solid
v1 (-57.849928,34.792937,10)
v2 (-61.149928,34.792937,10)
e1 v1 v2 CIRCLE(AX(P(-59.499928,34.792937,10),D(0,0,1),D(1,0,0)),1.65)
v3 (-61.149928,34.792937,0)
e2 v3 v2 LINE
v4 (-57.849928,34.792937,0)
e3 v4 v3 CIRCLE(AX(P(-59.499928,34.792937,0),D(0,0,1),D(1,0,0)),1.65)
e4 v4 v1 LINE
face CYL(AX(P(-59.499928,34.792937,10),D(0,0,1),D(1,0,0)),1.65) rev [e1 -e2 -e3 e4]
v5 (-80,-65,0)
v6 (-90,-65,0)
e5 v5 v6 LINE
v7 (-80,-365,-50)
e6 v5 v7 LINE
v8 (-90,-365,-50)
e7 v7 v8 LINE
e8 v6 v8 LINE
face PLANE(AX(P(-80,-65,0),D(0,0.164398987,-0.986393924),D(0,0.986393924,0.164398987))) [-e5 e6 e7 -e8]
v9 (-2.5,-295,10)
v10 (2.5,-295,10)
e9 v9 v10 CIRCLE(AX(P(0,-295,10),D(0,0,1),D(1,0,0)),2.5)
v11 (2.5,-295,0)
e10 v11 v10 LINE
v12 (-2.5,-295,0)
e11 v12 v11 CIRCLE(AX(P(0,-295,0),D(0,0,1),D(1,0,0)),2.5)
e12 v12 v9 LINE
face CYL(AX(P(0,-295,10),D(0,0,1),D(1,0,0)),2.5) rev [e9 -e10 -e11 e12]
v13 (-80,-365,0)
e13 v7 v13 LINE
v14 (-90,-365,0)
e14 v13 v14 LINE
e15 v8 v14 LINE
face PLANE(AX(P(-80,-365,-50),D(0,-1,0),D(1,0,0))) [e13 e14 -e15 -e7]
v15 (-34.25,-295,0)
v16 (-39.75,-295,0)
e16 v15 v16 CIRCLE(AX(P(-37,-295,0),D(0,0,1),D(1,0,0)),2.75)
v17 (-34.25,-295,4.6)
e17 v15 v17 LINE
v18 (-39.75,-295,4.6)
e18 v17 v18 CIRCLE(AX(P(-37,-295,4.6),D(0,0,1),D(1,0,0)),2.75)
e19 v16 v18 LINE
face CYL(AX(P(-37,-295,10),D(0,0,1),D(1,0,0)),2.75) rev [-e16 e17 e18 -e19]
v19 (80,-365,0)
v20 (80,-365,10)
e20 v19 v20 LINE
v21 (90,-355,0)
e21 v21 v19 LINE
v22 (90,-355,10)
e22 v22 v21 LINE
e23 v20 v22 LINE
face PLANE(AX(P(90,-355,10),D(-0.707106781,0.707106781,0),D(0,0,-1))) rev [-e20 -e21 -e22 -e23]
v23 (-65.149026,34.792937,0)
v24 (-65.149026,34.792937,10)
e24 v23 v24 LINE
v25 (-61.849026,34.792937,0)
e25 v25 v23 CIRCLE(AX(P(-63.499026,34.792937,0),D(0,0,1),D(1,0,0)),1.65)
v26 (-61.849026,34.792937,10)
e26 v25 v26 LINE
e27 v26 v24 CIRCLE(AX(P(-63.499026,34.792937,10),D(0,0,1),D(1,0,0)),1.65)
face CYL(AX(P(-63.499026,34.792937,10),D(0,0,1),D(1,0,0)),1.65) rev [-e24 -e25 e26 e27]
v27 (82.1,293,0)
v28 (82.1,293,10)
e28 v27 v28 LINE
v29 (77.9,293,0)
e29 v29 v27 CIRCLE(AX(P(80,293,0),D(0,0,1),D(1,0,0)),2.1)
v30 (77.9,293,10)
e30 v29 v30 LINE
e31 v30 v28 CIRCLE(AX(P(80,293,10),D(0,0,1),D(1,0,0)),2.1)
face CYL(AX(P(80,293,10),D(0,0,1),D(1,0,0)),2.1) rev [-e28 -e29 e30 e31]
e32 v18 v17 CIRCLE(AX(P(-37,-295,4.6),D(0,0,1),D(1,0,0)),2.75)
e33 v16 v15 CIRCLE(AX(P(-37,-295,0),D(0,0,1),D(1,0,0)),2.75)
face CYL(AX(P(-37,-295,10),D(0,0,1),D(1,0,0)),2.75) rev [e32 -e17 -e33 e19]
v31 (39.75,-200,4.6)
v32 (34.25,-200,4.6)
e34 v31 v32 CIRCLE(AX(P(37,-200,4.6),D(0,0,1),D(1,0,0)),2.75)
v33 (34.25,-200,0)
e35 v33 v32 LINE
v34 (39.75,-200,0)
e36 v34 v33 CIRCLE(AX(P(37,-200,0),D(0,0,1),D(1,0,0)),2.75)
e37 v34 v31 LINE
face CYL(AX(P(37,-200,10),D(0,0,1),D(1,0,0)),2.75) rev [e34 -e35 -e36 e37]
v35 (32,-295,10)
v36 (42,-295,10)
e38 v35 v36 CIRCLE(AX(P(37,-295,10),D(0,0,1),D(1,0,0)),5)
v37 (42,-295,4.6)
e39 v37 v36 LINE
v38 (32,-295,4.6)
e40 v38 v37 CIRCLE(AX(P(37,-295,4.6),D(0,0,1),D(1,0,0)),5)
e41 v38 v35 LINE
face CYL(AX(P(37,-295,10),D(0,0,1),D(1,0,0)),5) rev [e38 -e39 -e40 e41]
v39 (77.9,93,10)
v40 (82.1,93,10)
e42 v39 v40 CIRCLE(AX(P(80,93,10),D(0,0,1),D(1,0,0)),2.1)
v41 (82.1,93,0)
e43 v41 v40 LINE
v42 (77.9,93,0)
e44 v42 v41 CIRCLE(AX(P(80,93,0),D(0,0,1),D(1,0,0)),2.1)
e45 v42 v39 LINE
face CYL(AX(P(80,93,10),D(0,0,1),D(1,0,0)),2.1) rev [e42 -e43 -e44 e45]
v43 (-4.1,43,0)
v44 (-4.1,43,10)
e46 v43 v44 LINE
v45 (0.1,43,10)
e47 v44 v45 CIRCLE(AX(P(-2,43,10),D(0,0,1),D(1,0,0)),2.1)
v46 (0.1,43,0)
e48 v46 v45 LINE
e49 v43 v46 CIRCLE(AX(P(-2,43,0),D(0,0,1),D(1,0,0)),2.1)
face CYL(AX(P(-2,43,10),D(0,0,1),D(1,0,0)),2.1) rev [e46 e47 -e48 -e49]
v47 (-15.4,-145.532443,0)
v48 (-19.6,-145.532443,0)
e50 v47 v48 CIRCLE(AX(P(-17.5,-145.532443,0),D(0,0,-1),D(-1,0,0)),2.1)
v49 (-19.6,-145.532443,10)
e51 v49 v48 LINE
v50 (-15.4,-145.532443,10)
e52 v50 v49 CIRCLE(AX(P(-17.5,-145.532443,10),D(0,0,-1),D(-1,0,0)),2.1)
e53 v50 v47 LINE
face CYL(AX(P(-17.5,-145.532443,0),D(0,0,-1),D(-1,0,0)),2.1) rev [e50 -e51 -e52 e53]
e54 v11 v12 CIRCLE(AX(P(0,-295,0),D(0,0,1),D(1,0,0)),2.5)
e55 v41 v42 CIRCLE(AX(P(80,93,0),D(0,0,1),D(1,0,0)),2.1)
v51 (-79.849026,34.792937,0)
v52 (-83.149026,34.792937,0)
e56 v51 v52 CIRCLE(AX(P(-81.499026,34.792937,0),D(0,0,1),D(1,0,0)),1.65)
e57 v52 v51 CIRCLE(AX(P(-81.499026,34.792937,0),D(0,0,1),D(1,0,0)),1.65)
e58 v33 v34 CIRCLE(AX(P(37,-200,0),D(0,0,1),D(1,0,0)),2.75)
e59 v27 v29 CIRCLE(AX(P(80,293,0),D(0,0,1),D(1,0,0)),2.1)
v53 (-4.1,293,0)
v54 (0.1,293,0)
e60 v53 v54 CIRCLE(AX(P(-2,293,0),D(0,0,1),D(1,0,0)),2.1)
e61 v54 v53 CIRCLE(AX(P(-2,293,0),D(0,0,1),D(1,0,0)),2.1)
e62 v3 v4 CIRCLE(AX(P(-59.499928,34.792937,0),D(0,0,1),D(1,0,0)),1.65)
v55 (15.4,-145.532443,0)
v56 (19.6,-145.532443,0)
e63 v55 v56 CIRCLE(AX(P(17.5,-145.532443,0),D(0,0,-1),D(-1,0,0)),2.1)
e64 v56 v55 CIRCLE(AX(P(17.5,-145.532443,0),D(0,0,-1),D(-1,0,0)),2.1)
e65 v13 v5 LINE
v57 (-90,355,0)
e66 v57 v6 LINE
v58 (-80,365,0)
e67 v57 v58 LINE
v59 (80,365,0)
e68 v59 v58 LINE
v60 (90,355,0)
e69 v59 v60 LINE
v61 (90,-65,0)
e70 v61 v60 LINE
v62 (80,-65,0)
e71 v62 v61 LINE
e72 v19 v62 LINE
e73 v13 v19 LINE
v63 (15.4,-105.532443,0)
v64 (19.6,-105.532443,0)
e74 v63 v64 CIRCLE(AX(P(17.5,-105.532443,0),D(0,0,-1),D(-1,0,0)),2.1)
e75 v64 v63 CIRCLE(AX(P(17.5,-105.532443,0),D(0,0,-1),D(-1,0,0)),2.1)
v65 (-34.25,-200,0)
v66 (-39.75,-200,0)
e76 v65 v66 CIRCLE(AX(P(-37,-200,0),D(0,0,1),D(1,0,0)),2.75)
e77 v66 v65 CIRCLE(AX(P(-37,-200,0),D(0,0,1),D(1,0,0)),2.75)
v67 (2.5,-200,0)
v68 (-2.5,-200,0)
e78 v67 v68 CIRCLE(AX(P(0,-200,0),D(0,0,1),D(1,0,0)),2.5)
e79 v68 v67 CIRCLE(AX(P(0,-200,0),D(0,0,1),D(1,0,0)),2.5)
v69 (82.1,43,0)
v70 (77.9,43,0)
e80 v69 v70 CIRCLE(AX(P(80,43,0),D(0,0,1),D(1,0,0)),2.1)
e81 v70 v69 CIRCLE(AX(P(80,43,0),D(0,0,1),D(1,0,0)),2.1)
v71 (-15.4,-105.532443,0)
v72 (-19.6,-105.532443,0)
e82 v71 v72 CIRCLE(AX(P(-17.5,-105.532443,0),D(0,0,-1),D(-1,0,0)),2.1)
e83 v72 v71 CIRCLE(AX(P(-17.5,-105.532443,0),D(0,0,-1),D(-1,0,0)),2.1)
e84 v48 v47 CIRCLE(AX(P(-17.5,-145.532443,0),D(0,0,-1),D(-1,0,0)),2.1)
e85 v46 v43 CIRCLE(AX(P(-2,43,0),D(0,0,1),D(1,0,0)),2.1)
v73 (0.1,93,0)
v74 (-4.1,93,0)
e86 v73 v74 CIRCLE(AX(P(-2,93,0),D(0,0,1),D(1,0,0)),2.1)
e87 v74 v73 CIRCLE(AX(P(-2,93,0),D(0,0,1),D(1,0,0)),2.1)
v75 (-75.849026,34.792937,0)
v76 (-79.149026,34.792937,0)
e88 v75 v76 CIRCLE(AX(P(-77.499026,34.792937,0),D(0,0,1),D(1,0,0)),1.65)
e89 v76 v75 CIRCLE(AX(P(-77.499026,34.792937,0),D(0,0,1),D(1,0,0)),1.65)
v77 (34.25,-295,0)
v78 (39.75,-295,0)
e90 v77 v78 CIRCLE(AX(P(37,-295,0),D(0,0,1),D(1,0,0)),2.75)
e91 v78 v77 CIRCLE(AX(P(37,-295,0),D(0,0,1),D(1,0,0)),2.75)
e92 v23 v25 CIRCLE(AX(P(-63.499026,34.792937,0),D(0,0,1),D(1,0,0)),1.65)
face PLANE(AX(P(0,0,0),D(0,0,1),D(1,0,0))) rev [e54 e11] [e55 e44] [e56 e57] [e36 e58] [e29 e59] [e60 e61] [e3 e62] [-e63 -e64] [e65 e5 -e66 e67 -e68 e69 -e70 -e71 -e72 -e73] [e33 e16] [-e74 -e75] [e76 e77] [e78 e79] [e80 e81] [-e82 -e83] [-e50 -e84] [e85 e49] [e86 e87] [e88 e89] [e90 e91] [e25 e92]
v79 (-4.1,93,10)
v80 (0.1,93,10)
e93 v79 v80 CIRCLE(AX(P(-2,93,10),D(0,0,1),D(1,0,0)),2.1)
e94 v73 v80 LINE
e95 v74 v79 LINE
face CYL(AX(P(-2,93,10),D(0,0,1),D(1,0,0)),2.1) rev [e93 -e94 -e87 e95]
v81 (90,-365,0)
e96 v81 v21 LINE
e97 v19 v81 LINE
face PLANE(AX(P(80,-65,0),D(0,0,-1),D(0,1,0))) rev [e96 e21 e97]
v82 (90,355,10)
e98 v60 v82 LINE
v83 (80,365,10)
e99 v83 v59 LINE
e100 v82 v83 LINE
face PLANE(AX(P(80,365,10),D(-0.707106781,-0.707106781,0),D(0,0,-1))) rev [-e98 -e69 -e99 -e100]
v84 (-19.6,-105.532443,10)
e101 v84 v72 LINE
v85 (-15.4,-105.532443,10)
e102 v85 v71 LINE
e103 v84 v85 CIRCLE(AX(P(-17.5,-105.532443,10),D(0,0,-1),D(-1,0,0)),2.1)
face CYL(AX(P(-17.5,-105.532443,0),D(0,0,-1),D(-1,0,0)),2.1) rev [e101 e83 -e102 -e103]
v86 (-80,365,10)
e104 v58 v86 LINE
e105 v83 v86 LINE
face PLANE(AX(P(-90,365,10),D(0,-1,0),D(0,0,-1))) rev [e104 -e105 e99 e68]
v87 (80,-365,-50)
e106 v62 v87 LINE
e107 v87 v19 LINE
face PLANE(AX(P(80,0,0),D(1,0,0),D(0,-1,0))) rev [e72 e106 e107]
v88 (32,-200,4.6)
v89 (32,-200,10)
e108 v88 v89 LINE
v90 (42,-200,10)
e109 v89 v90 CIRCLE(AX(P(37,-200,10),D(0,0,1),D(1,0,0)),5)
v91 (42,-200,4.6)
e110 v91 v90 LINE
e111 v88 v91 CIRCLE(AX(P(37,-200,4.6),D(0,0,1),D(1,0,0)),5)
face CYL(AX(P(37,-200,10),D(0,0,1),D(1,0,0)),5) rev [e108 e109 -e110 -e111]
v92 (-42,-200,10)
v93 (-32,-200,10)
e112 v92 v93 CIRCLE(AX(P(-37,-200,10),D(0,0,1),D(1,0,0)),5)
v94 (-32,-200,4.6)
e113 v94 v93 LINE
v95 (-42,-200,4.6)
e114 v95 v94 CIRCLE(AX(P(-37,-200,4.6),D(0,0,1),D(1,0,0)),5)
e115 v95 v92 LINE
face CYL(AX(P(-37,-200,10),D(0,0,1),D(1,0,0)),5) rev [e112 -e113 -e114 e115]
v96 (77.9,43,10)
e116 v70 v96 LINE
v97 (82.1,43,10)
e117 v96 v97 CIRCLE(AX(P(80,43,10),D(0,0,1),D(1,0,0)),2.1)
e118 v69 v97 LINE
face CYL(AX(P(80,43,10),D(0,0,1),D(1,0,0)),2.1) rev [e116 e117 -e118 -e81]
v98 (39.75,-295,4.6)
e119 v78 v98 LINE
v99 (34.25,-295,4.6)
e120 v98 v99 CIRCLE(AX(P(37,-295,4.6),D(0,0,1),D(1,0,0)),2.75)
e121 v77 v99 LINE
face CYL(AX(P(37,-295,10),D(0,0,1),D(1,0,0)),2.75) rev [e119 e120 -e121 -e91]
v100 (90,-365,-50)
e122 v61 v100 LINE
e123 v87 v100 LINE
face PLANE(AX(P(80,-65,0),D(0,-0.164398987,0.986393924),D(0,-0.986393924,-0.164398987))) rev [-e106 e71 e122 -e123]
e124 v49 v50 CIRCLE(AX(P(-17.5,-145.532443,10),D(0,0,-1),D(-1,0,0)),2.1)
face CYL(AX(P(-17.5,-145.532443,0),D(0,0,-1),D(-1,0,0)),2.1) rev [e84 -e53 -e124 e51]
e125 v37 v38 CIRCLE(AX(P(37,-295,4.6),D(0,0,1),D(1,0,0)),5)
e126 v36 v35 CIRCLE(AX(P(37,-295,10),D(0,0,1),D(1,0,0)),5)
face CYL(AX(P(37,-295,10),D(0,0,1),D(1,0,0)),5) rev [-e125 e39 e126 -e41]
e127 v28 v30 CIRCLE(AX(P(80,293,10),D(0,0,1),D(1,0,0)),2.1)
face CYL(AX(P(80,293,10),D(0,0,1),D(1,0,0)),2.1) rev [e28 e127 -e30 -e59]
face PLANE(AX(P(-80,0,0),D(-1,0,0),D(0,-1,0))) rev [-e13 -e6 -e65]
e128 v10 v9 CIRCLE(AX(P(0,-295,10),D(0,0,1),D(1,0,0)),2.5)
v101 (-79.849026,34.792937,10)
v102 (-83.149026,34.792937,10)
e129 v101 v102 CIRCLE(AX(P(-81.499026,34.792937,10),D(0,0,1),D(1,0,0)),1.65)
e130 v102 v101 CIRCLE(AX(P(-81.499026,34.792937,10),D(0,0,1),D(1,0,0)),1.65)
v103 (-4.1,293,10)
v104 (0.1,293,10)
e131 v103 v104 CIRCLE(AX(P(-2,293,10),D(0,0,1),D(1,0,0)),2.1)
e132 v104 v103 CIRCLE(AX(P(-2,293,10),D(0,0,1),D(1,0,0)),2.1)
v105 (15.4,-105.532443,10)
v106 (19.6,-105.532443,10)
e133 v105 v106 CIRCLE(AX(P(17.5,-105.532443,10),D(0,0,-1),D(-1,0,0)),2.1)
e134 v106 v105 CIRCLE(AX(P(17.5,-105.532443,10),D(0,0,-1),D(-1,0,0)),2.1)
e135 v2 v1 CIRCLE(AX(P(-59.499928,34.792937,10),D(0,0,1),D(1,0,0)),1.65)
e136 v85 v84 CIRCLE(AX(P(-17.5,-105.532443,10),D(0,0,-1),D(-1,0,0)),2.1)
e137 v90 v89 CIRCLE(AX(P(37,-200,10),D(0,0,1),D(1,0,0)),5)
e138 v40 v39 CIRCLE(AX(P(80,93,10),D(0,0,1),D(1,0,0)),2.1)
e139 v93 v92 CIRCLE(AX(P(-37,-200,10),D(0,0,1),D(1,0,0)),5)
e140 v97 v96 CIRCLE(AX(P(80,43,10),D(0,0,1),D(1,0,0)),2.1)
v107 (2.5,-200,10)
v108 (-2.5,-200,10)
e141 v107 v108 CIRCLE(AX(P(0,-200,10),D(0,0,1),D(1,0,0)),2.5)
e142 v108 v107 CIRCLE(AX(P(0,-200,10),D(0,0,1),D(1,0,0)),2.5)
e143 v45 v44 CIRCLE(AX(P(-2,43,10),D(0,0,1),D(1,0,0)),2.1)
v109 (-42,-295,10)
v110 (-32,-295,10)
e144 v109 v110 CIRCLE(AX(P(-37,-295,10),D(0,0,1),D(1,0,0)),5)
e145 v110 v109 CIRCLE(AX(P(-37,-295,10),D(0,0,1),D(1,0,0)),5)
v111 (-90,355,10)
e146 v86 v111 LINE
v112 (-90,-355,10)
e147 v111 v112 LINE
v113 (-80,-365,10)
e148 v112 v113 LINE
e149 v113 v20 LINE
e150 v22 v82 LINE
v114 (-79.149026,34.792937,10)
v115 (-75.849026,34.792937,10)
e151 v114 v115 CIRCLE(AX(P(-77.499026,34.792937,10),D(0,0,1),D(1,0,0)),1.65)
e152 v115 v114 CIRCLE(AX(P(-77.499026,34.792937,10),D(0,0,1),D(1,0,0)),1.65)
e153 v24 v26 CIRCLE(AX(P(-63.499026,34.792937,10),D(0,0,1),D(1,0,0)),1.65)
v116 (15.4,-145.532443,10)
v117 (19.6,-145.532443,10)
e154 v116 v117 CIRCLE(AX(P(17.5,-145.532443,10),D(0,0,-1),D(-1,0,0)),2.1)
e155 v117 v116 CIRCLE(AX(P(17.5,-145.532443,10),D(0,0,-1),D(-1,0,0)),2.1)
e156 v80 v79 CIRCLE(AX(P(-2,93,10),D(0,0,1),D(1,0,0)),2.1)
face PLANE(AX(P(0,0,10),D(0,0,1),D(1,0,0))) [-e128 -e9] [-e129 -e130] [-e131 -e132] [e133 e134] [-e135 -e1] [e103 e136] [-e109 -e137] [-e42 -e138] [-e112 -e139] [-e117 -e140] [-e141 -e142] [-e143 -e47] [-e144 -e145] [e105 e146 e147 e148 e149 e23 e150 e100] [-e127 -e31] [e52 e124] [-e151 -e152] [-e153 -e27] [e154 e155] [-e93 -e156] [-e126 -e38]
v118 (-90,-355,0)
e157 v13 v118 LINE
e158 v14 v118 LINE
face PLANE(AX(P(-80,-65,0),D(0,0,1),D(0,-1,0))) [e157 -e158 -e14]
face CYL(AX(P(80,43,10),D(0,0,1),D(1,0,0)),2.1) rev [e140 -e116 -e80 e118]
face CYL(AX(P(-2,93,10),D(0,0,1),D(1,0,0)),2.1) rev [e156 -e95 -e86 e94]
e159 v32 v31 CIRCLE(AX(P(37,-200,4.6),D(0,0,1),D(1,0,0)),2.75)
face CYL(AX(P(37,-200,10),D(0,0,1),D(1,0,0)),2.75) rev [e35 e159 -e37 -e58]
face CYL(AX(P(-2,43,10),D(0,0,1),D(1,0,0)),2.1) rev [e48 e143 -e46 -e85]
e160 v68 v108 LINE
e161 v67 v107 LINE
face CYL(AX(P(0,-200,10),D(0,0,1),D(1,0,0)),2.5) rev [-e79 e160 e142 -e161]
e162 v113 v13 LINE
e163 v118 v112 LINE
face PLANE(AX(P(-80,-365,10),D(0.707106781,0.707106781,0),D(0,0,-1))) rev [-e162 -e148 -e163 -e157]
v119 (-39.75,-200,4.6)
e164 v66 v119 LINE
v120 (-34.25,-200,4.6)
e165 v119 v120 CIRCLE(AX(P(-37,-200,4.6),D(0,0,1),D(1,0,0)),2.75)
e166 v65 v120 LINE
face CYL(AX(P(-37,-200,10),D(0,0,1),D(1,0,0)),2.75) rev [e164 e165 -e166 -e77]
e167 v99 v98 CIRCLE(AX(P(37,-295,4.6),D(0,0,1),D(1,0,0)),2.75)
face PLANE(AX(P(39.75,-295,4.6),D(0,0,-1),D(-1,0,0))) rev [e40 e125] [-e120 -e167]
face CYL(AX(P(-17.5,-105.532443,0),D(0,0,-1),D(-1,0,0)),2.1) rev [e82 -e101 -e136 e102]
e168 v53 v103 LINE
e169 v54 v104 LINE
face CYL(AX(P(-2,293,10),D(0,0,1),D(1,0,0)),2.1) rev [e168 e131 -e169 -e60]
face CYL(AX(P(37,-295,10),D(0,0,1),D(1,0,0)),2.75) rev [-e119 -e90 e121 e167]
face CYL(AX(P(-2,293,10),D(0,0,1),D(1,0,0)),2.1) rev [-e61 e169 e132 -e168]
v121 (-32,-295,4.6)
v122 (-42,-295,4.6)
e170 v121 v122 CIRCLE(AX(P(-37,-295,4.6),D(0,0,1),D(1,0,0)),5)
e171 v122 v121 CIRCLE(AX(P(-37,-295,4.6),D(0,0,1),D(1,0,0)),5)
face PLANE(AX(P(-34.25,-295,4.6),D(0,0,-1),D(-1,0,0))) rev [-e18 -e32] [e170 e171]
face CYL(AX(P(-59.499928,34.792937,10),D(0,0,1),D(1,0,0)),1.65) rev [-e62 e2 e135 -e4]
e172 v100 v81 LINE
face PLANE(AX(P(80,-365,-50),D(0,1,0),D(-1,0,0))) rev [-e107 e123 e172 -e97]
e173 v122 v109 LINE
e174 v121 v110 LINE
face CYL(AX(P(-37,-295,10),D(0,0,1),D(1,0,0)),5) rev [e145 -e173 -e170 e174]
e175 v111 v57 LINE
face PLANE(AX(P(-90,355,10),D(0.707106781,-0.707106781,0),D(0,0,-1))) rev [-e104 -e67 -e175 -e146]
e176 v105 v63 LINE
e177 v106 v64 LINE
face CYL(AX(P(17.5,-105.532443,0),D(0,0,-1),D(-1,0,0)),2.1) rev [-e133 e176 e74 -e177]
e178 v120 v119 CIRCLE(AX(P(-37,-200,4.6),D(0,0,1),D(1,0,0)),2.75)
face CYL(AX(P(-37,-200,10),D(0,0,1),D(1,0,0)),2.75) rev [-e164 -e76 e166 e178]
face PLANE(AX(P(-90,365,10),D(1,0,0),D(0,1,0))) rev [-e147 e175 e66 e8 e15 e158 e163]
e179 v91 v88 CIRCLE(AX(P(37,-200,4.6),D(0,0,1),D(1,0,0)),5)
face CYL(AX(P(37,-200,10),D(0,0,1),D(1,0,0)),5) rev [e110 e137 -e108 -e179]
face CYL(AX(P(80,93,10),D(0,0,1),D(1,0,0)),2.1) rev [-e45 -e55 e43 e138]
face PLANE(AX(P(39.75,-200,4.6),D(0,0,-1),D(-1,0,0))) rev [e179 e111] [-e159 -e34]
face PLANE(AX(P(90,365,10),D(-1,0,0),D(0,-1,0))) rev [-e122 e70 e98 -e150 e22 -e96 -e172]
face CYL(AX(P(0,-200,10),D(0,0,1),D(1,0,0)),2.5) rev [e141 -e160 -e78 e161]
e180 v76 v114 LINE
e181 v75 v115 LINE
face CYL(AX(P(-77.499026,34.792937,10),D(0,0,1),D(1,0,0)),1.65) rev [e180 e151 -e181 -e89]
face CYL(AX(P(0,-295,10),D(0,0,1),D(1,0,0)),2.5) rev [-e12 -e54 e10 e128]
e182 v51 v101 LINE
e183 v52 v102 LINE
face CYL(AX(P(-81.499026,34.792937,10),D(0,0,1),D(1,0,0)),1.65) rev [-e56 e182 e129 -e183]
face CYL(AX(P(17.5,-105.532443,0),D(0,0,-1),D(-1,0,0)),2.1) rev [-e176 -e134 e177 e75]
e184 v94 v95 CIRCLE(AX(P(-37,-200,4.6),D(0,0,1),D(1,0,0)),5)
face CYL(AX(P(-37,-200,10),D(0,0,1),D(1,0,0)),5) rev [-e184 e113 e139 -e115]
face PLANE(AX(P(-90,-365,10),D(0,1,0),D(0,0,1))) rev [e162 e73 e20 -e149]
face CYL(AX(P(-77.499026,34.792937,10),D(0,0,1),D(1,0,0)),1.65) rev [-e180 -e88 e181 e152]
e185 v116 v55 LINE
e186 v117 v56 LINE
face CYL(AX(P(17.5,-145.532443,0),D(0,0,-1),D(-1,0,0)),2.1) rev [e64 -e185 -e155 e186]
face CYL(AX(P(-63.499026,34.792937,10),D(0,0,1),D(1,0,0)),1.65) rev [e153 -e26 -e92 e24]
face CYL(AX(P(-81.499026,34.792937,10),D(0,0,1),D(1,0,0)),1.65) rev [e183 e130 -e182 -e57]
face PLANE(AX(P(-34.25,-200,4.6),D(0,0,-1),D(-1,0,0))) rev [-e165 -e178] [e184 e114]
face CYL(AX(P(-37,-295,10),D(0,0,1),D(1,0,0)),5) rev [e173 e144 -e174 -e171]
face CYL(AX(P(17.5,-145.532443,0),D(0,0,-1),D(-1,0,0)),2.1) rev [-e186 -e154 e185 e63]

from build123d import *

# Parameters (mm, degrees)
SKETCH_1_W                   = 180
SKETCH_1_H                   = 730
EXTRUDE_1_DEPTH              = 10
HOLE_WIZARD_M5_1_D           = 5.5
HOLE_WIZARD_M5_1_CBORE_D     = 10
HOLE_WIZARD_M5_1_CBORE_DEPTH = 5.4
MM_0_D                       = 5
CHAMFER_1_SIZE               = 10
HOLE_WIZARD_M5_2_D           = 4.2
HOLE_WIZARD_M5_3_D           = 4.2
HOLE_WIZARD_M4_1_D           = 3.3
EXTRUDE_2_DEPTH              = 10


with BuildPart() as part:
    # 草图1 → 凸台-拉伸1 (new body)
    with BuildSketch(Plane.XY):
        Rectangle(SKETCH_1_W, SKETCH_1_H)
    extrude(amount=EXTRUDE_1_DEPTH)

    # M5 六角凹头螺钉的柱形沉头孔1 (through all)
    with Locations(Plane.XY.offset(10)):
        with Locations((-37, -200), (37, -200), (-37, -295), (37, -295)):
            CounterBoreHole(HOLE_WIZARD_M5_1_D / 2, HOLE_WIZARD_M5_1_CBORE_D / 2, HOLE_WIZARD_M5_1_CBORE_DEPTH)

    # 大小mm 暗销孔0 (through all)
    with Locations(Plane.XY.offset(10)):
        with Locations((0, -200), (0, -295)):
            Hole(MM_0_D / 2)

    # 倒角1
    chamfer_1_edges = [part.edges().sort_by_distance(p)[0] for p in [
        (90, -365, 5),
        (-90, -365, 5),
        (-90, 365, 5),
        (90, 365, 5),
    ]]
    chamfer(chamfer_1_edges, length=CHAMFER_1_SIZE)

    # M5 螺纹孔2 (through all)
    with Locations(Plane.XY.offset(10)):
        with Locations((80, 293), (-2, 293), (80, 93), (80, 43), (-2, 43), (-2, 93)):
            Hole(HOLE_WIZARD_M5_2_D / 2)

    # M5 螺纹孔3 (through all)
    with Locations(Plane(origin=(0, 0, 0), x_dir=(-1, 0, 0), z_dir=(0, 0, -1))):
        with Locations((-17.5, -105.532443279), (-17.5, -145.532443279), (17.5, -105.532443279), (17.5, -145.532443279)):
            Hole(HOLE_WIZARD_M5_3_D / 2)

    # M4 螺纹孔1 (through all)
    with Locations(Plane.XY.offset(10)):
        with Locations((-81.499026454, 34.792936996), (-59.499927509, 34.792936996), (-77.499026454, 34.792936996), (-63.499026454, 34.792936996)):
            Hole(HOLE_WIZARD_M4_1_D / 2)

    # 草图12 → 凸台-拉伸2 (add)
    with BuildSketch(Plane.ZY.offset(90)):
        Polygon((0, -65), (-50, -365), (0, -365), align=None)
    extrude_2 = extrude(amount=-EXTRUDE_2_DEPTH)

    # 镜向1: 凸台-拉伸2 across plane
    add(extrude_2.mirror(Plane(origin=(0, 0, 0), x_dir=(0, 0, 1), z_dir=(1, 0, 0))))


solid = part.part
